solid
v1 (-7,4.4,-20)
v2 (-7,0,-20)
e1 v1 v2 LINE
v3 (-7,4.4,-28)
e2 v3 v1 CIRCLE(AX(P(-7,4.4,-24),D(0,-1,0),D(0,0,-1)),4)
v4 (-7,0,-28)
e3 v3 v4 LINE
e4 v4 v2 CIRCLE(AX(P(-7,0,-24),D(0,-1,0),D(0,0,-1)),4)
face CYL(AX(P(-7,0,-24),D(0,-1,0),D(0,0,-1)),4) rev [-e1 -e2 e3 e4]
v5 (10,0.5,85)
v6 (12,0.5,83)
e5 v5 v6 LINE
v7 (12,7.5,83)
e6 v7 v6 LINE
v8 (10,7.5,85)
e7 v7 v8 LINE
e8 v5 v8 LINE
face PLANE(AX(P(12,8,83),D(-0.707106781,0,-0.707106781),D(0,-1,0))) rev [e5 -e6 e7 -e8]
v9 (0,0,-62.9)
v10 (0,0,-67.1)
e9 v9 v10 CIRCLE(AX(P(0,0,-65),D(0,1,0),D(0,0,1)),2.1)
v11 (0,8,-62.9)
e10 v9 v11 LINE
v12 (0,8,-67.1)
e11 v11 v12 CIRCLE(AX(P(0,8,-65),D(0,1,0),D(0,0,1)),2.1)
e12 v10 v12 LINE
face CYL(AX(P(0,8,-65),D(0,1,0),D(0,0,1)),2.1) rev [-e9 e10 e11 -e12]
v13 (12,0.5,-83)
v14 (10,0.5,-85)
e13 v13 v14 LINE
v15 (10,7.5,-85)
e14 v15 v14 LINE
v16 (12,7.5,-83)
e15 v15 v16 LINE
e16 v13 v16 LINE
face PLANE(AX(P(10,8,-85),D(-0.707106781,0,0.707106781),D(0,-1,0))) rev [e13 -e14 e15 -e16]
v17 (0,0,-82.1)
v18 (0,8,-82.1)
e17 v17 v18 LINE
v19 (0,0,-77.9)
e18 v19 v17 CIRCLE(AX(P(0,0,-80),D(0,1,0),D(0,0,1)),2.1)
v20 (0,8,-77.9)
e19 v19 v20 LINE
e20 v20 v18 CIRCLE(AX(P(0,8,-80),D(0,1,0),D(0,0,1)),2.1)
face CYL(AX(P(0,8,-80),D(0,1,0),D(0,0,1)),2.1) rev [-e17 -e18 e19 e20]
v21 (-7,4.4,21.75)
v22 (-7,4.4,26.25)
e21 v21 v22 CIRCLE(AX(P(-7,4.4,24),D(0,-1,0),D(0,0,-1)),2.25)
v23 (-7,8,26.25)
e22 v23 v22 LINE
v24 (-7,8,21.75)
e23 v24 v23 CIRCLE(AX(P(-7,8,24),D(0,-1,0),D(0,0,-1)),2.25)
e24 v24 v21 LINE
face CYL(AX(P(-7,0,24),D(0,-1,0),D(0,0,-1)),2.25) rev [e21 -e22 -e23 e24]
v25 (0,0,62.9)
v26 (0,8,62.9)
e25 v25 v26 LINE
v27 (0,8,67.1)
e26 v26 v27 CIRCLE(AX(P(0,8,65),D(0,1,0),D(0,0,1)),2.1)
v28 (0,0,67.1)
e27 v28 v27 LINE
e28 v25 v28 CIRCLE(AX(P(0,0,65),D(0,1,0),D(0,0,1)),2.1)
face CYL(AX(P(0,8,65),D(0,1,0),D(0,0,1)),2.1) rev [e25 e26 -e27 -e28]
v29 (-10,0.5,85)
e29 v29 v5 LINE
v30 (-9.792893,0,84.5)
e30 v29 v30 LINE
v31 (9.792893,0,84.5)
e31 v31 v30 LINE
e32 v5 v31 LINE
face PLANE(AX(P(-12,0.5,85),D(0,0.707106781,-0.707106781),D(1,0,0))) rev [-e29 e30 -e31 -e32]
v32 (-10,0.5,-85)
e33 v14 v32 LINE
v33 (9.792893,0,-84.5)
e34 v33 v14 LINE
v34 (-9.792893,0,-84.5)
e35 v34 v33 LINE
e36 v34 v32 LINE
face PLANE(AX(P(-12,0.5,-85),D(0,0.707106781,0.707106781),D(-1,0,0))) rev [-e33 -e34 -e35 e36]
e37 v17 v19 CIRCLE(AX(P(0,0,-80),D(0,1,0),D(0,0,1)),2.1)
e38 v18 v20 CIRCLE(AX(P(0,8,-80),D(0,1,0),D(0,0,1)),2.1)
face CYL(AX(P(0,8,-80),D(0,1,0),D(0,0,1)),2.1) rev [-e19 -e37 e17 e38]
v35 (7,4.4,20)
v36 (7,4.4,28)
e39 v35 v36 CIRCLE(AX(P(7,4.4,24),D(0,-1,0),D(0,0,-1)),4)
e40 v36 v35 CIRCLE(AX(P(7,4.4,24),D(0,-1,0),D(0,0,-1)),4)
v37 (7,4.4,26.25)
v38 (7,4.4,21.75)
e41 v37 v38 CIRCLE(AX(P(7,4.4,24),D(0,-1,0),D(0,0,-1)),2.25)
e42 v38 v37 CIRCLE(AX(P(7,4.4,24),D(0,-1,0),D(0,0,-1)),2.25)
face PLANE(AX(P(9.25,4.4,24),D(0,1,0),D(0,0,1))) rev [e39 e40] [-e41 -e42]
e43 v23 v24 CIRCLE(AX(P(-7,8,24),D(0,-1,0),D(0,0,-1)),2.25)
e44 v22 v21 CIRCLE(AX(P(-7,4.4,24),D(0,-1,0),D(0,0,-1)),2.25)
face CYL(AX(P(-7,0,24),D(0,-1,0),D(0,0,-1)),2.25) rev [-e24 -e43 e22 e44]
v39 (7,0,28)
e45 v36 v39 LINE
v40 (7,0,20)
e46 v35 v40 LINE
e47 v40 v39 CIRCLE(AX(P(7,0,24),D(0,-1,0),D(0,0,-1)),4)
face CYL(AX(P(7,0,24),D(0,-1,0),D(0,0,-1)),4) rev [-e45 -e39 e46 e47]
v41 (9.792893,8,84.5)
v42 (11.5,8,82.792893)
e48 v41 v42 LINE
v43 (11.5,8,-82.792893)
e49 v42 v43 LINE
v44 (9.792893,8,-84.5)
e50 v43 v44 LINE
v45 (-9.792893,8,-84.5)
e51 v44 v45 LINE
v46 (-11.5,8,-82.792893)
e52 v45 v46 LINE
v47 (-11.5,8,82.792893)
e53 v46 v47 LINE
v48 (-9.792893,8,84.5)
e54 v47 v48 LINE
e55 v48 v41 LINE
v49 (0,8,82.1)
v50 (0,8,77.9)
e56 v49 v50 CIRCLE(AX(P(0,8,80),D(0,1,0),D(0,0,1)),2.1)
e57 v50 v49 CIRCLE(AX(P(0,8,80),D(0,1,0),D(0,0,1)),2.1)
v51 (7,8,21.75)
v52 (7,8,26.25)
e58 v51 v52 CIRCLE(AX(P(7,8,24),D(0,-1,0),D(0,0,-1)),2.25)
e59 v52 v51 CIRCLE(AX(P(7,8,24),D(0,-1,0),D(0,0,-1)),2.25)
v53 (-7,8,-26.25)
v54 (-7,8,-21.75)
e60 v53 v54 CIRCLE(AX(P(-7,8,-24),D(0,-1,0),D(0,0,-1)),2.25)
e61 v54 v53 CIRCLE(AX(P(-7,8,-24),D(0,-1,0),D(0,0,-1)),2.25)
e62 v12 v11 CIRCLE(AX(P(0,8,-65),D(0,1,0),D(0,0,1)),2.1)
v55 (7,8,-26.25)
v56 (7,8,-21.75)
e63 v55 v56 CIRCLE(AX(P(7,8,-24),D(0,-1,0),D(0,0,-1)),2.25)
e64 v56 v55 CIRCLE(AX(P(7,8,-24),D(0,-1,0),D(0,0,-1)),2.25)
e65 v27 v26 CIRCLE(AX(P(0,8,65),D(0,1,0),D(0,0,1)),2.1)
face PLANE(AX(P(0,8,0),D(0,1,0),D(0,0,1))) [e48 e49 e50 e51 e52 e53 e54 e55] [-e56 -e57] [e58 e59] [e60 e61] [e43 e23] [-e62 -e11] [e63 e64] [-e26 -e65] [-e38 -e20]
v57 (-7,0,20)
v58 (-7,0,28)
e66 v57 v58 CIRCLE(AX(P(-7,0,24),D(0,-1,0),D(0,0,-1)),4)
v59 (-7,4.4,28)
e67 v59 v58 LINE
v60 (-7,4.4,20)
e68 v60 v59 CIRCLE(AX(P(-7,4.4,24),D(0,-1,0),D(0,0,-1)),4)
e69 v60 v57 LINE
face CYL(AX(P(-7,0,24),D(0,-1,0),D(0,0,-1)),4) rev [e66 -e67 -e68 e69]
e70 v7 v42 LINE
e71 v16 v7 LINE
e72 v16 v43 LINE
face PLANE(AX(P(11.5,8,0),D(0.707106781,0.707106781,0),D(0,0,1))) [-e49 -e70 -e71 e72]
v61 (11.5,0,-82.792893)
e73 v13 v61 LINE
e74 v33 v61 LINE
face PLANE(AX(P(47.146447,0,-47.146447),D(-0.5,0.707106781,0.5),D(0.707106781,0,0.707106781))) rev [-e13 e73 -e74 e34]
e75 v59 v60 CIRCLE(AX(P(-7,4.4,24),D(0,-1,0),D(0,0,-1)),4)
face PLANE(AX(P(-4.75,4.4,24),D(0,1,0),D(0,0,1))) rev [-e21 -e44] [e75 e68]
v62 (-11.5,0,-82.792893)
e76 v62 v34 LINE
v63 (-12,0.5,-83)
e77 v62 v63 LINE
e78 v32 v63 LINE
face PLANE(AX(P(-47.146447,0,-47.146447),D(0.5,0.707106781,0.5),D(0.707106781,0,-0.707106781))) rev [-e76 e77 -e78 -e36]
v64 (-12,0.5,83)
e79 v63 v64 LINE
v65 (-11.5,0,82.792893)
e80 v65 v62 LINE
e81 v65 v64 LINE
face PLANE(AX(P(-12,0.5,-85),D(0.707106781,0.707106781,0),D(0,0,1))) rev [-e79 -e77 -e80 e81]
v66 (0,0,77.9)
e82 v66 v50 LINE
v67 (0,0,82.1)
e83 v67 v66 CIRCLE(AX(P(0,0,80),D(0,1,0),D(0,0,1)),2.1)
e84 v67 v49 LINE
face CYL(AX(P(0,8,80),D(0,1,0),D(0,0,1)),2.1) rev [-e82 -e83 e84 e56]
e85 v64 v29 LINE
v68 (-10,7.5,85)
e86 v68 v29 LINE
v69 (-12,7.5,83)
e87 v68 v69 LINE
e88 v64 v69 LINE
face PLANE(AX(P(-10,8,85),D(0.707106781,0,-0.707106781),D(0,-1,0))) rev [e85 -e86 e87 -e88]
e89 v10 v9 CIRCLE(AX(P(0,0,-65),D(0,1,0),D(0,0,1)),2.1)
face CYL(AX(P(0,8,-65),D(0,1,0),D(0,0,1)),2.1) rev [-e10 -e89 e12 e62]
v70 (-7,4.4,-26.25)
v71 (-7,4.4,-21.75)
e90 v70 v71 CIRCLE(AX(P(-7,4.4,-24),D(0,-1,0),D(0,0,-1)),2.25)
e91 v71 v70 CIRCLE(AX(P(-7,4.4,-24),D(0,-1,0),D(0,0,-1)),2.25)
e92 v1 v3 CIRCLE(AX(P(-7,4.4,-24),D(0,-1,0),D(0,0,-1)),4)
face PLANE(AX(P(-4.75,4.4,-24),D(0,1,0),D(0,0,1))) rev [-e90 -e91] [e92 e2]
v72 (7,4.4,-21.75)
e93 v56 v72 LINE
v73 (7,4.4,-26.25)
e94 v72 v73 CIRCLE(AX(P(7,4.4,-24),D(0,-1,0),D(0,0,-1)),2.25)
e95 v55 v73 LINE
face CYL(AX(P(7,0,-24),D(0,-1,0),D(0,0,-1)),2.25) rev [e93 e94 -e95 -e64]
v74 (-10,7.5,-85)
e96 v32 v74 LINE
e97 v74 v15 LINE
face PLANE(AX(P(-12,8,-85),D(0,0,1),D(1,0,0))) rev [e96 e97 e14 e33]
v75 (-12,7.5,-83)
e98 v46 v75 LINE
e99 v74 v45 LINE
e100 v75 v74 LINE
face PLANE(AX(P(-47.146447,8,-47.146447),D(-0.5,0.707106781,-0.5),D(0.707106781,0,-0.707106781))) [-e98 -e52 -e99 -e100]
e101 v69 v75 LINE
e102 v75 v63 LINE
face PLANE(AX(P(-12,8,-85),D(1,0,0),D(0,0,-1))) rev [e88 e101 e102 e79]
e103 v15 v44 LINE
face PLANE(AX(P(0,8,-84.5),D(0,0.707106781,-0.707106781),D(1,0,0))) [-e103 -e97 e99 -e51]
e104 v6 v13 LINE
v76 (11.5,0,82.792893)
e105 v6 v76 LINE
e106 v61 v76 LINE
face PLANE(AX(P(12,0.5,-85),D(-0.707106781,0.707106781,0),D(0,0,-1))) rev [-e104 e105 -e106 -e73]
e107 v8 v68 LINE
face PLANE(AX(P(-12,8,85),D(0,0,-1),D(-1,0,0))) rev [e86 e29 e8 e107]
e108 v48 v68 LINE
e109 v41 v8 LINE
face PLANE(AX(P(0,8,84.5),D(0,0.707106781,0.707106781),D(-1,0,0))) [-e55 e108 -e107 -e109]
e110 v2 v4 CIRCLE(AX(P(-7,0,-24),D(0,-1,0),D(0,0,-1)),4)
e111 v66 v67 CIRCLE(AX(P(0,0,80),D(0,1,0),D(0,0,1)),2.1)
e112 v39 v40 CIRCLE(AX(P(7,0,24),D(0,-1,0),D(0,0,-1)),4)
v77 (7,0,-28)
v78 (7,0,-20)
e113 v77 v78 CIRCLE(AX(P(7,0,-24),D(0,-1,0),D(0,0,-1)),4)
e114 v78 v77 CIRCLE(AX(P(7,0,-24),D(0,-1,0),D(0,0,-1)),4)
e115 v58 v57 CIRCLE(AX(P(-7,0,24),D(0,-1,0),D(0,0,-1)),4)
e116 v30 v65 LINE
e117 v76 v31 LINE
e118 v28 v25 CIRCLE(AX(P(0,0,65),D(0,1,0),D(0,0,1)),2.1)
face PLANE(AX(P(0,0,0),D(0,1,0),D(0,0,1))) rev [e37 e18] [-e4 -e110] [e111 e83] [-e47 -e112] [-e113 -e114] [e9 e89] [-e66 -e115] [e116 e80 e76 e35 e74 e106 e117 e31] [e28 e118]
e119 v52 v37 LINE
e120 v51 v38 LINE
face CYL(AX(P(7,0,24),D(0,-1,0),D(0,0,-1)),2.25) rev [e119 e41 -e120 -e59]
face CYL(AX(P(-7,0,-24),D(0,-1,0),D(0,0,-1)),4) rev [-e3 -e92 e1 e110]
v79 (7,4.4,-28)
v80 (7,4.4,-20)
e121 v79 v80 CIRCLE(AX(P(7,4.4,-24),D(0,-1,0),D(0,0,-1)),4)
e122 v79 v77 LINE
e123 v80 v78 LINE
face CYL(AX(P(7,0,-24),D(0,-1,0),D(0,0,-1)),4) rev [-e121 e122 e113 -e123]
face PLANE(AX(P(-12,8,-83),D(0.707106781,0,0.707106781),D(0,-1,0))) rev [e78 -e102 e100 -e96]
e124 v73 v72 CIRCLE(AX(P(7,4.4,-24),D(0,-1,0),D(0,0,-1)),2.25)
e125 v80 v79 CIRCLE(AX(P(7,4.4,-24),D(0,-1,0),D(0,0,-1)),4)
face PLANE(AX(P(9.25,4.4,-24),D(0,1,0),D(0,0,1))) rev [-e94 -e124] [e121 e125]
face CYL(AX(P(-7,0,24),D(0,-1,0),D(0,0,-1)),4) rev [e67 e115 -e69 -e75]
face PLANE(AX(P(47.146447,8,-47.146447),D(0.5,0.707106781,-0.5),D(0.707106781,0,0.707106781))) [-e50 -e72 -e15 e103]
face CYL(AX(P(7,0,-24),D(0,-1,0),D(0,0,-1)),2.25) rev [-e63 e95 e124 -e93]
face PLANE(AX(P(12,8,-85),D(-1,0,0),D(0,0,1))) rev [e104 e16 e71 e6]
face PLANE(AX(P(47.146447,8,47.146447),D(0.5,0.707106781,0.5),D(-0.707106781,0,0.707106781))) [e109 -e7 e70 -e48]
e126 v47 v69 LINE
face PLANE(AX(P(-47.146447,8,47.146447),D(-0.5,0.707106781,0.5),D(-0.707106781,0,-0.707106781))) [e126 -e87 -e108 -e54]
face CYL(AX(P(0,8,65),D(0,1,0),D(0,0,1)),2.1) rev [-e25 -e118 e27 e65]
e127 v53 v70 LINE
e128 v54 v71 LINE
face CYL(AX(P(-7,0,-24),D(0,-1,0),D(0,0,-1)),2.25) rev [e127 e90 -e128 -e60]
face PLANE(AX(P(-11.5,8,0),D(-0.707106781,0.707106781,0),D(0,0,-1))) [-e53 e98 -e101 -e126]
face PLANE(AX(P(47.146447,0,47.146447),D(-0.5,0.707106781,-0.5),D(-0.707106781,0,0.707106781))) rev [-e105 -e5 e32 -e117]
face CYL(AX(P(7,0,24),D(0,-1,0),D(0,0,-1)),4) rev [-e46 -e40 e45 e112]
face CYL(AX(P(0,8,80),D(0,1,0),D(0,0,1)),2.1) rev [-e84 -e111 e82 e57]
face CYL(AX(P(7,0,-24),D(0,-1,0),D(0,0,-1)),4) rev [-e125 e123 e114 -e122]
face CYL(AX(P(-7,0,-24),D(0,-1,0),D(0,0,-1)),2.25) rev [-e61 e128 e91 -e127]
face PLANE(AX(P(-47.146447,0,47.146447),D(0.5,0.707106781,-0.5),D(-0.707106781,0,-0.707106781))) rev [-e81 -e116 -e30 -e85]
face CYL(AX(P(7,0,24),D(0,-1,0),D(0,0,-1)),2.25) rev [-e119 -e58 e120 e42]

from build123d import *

# Parameters (mm, degrees)
SKETCH_1_W                   = 24
SKETCH_1_H                   = 170
EXTRUDE_1_DEPTH              = 8
HOLE_WIZARD_M4_1_D           = 4.5
HOLE_WIZARD_M4_1_CBORE_D     = 8
HOLE_WIZARD_M4_1_CBORE_DEPTH = 4.4
HOLE_WIZARD_M5_1_D           = 4.2
HOLE_WIZARD_M5_1_DEPTH       = 12.4
HOLE_WIZARD_M5_1_TIP         = 1.2618073
CHAMFER_1_SIZE               = 2
CHAMFER_2_SIZE               = 0.5


with BuildPart() as part:
    # 草图1 → 凸台-拉伸1 (new body)
    with BuildSketch(Plane(origin=(0, 0, 0), x_dir=(1, 0, 0), z_dir=(0, 1, 0))):
        Rectangle(SKETCH_1_W, SKETCH_1_H)
    extrude(amount=EXTRUDE_1_DEPTH)

    # M4 六角凹头螺钉的柱形沉头孔1 (through all)
    with Locations(Plane(origin=(0, 0, 0), x_dir=(-1, 0, 0), z_dir=(0, -1, 0))):
        with Locations((-7, 24), (7, 24), (-7, -24), (7, -24)):
            CounterBoreHole(HOLE_WIZARD_M4_1_D / 2, HOLE_WIZARD_M4_1_CBORE_D / 2, HOLE_WIZARD_M4_1_CBORE_DEPTH)

    # M5 螺纹孔1
    with Locations(Plane(origin=(0, 8, 0), x_dir=(1, 0, 0), z_dir=(0, 1, 0))):
        with Locations((0, 80), (0, -80), (0, -65), (0, 65)):
            Hole(HOLE_WIZARD_M5_1_D / 2, depth=HOLE_WIZARD_M5_1_DEPTH)
            with Locations((0, 0, -(HOLE_WIZARD_M5_1_DEPTH + HOLE_WIZARD_M5_1_TIP / 2))):  # 118° drill point
                Cone(0, HOLE_WIZARD_M5_1_D / 2, HOLE_WIZARD_M5_1_TIP, mode=Mode.SUBTRACT)

    # 倒角1
    chamfer_1_edges = [part.edges().sort_by_distance(p)[0] for p in [
        (12, 4, 85),
        (-12, 4, 85),
        (-12, 4, -85),
        (12, 4, -85),
    ]]
    chamfer(chamfer_1_edges, length=CHAMFER_1_SIZE)

    # 倒角2
    chamfer_2_edges = [part.edges().sort_by_distance(p)[0] for p in [
        (-12, 0, 0),
        (-12, 8, 0),
        (12, 0, 0),
        (0, 0, 85),
        (0, 0, -85),
        (11, 0, 84),
        (-11, 0, 84),
        (11, 0, -84),
        (-11, 0, -84),
        (0, 8, -85),
        (12, 8, 0),
        (0, 8, 85),
        (11, 8, 84),
        (-11, 8, 84),
        (11, 8, -84),
        (-11, 8, -84),
    ]]
    chamfer(chamfer_2_edges, length=CHAMFER_2_SIZE)


solid = part.part
